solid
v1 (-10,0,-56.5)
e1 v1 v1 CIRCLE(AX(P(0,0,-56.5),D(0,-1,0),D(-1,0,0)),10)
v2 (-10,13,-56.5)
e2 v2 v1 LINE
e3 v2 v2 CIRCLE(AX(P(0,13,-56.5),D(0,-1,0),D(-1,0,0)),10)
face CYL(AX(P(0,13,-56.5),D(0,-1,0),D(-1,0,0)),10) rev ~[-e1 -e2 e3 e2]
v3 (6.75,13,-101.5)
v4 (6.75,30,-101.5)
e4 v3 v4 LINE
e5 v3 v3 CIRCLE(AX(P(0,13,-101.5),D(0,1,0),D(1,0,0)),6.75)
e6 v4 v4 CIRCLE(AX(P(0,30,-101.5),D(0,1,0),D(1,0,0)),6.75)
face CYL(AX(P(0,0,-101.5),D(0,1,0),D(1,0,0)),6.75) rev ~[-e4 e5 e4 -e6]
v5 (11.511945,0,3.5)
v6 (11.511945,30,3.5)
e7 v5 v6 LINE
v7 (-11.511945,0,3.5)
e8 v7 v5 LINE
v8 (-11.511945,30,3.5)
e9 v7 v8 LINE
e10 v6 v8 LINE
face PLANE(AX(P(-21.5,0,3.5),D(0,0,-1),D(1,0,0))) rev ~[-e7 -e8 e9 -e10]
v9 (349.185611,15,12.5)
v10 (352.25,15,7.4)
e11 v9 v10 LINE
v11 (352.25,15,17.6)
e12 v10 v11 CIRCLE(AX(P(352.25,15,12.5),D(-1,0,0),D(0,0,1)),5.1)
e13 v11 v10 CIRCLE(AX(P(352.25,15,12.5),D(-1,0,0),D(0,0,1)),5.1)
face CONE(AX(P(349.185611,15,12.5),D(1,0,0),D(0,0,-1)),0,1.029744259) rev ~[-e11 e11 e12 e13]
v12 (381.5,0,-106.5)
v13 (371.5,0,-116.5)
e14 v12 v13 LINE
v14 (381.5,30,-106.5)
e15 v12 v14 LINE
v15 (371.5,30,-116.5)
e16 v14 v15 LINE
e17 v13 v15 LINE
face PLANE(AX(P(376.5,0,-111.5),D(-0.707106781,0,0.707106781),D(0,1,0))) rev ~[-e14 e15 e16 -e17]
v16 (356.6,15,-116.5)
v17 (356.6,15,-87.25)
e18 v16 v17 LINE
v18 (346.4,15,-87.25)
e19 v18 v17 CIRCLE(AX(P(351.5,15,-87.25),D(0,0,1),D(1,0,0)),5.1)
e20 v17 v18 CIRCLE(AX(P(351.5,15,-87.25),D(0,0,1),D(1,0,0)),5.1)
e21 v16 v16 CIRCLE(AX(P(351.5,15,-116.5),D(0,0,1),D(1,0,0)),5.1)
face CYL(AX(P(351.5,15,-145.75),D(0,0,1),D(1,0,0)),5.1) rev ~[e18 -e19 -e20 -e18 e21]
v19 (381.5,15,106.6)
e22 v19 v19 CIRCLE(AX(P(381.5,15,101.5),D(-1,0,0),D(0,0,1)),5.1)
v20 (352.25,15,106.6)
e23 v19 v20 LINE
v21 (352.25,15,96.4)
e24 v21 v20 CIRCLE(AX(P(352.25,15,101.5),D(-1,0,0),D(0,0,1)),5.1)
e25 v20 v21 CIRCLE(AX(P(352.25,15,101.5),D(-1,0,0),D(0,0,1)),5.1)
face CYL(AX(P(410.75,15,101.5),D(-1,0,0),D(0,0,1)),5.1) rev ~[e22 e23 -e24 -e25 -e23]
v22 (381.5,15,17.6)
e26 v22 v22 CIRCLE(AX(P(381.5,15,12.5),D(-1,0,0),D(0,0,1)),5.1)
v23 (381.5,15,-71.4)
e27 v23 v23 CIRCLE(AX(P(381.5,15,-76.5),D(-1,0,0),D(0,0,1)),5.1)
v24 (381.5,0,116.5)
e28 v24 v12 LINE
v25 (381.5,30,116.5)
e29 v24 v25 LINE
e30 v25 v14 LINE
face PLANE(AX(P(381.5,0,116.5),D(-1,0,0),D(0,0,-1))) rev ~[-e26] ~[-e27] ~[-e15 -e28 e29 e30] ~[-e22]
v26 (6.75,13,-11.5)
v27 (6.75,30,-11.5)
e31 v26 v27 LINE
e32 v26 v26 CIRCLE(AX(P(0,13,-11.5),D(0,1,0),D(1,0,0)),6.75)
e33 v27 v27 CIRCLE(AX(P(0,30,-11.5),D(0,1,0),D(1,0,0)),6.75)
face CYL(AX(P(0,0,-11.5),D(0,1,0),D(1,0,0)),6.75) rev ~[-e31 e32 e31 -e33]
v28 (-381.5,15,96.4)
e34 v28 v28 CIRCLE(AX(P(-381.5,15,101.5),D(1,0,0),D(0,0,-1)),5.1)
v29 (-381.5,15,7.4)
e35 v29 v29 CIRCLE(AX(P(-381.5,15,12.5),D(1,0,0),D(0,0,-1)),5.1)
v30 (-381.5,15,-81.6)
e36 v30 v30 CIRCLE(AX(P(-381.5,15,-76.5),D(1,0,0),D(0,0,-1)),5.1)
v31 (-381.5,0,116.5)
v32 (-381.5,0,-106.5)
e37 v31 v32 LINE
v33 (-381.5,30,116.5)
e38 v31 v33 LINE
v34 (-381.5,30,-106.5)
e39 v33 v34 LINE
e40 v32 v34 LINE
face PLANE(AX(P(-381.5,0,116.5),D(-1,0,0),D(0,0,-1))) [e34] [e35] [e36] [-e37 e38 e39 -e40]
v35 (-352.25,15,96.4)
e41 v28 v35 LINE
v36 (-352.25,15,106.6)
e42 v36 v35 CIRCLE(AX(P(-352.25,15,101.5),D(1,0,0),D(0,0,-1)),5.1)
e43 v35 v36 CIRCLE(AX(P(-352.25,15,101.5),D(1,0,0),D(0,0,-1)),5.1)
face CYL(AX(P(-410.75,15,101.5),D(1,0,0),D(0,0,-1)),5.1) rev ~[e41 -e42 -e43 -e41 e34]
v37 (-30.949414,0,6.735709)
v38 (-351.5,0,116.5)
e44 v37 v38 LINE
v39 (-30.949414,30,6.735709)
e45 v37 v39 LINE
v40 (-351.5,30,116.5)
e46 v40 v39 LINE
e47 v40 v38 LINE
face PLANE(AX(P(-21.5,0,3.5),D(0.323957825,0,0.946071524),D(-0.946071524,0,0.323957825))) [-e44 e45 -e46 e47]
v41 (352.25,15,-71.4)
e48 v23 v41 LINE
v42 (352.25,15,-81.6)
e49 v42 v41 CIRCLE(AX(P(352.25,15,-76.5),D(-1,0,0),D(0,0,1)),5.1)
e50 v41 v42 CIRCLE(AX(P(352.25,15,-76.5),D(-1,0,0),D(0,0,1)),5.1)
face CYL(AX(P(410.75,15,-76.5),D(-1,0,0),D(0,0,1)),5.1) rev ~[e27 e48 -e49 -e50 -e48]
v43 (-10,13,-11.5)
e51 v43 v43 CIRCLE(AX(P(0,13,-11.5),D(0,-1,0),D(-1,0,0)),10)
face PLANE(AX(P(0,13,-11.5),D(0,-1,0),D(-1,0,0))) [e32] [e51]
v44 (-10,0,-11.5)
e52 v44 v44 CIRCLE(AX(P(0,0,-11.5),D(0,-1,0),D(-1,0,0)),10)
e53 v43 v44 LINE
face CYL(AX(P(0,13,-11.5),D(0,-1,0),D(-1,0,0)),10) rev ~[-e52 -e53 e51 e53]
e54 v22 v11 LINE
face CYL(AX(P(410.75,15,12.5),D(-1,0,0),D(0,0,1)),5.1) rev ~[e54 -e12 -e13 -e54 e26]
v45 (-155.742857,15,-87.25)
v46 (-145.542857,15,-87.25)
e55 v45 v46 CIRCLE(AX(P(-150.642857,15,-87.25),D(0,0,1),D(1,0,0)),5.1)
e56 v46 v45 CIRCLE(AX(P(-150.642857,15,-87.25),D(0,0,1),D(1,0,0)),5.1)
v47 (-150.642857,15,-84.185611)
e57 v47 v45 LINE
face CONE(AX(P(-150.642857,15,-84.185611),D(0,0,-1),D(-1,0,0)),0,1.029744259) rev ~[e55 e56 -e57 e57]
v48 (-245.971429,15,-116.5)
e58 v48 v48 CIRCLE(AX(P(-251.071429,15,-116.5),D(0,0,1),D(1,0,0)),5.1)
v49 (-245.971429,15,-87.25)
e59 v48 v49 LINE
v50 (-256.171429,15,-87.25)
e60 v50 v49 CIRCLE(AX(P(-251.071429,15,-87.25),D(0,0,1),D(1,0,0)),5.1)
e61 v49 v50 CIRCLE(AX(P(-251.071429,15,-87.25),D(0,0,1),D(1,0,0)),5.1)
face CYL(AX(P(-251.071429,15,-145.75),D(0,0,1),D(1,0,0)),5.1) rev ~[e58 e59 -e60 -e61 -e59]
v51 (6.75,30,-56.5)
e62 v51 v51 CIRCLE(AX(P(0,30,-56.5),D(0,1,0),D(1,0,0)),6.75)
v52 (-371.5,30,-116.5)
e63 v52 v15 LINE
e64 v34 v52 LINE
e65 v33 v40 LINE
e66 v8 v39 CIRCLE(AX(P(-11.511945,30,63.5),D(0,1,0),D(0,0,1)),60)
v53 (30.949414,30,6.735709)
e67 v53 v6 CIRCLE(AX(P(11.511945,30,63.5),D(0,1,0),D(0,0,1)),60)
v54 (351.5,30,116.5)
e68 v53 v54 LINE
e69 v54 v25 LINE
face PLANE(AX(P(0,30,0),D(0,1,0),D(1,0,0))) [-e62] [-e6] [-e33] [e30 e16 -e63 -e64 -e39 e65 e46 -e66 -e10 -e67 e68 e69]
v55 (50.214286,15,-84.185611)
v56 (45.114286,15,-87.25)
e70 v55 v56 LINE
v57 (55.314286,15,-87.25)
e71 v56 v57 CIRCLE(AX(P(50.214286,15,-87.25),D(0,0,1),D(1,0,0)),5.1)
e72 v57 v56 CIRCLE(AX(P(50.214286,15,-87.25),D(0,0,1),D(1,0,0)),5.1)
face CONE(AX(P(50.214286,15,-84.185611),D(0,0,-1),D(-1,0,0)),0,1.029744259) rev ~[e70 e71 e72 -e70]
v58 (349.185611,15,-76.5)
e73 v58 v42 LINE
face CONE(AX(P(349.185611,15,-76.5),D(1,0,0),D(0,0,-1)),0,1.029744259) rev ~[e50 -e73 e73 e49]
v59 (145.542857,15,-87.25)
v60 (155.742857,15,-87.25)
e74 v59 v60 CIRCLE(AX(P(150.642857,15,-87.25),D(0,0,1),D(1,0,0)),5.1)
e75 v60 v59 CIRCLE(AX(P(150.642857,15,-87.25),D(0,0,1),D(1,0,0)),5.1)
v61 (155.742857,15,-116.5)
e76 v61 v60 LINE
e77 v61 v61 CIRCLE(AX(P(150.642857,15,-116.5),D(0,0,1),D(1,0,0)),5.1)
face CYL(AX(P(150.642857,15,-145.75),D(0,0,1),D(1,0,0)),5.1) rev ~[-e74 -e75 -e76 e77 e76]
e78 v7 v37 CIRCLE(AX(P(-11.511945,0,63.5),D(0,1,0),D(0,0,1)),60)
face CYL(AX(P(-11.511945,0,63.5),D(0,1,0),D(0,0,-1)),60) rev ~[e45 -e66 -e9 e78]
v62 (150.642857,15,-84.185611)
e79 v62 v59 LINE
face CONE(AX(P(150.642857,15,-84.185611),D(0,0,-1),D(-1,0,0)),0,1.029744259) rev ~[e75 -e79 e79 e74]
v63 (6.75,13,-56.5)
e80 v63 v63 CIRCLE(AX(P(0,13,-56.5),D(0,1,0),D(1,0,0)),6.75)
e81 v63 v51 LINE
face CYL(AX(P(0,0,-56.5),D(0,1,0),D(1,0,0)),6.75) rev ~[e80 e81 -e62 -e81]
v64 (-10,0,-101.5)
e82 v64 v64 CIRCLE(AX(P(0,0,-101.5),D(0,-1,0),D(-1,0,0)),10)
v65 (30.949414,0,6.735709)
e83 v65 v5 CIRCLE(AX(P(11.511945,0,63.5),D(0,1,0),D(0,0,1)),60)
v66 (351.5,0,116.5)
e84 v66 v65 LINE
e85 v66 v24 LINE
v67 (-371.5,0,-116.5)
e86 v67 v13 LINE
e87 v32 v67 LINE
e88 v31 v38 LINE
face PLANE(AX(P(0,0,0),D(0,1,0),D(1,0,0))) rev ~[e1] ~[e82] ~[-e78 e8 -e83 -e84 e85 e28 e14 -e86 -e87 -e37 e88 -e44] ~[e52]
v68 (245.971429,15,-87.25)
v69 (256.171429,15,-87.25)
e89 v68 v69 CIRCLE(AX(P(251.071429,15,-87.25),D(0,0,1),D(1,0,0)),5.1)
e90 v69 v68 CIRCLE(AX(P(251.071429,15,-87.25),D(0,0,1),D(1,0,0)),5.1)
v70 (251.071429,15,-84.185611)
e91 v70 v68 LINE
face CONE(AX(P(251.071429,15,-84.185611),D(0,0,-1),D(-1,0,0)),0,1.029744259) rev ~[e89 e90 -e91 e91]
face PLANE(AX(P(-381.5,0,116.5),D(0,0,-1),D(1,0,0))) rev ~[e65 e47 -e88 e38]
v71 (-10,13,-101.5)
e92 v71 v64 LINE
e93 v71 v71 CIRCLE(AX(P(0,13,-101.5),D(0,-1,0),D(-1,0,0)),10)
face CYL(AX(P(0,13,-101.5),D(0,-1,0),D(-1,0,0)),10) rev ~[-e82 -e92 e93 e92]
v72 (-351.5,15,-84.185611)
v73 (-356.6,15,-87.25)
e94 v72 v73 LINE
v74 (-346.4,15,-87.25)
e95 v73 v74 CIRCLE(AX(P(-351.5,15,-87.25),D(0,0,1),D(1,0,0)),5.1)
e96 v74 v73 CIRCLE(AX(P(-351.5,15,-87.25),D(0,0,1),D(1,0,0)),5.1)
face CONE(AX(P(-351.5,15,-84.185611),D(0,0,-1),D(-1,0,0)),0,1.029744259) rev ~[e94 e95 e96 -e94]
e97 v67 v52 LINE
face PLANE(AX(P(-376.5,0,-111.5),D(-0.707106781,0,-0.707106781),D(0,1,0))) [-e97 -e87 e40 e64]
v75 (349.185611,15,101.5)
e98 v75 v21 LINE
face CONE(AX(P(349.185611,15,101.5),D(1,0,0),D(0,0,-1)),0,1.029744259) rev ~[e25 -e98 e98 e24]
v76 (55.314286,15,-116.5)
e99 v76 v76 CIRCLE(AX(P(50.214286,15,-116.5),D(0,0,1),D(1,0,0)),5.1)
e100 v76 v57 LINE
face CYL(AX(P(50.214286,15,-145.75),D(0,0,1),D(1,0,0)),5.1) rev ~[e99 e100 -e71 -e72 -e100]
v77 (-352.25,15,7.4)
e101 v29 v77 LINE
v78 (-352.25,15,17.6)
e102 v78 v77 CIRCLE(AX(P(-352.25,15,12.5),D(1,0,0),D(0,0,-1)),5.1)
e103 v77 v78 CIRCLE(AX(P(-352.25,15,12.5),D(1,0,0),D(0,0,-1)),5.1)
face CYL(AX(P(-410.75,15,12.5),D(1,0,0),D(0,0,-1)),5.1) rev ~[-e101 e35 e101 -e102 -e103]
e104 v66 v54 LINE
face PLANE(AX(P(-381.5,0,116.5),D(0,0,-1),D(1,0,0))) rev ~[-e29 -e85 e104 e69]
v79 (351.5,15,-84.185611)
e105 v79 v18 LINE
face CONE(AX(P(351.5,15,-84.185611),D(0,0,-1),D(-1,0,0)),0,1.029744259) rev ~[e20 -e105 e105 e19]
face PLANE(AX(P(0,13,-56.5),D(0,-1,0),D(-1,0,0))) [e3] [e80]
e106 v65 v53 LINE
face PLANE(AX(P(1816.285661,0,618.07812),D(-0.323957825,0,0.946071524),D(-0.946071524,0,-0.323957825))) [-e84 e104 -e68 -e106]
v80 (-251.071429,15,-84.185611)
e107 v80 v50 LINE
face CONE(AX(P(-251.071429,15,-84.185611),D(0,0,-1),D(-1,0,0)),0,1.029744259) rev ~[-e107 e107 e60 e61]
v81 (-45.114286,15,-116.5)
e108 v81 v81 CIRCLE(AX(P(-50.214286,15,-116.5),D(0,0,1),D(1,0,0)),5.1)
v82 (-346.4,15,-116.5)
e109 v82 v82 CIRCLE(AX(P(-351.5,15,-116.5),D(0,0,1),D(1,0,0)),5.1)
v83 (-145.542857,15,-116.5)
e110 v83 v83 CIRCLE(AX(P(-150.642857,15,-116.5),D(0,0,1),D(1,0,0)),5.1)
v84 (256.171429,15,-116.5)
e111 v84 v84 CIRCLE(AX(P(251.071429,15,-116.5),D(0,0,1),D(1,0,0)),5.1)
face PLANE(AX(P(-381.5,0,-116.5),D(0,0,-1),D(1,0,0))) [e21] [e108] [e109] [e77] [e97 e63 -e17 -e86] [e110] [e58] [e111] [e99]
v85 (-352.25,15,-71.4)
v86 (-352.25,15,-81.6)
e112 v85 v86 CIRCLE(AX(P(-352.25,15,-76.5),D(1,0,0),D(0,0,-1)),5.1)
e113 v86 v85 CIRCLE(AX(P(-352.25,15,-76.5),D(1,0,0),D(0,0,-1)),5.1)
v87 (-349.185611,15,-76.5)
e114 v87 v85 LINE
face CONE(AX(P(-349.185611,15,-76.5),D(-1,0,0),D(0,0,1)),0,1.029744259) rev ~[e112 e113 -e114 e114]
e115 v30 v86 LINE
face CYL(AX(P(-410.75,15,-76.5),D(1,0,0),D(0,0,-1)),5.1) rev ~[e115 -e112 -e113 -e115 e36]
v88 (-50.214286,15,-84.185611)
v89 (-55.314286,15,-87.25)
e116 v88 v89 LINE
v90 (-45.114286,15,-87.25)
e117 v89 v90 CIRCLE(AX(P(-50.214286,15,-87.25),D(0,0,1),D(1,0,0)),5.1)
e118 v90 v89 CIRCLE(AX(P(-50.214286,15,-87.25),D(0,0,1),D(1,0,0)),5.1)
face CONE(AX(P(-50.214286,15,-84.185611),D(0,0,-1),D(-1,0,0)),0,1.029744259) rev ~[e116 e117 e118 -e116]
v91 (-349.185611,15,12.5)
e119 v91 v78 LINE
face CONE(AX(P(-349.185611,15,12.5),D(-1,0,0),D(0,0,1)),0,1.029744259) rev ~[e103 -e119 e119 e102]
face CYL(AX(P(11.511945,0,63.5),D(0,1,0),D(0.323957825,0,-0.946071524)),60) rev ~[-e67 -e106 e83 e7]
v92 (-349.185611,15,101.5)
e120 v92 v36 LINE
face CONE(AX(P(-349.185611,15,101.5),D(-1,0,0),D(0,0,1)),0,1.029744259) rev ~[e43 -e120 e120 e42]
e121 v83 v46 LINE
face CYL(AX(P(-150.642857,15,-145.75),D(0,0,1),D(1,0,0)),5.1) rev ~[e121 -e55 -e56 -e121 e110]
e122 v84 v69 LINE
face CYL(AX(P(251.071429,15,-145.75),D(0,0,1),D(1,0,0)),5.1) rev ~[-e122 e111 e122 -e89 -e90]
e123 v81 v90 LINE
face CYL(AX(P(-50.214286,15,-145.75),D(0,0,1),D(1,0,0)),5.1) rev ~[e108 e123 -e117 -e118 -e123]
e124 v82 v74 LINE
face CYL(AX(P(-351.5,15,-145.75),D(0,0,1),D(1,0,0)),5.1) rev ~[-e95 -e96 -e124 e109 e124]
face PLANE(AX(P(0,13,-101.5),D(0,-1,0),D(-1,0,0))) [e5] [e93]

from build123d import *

# Parameters (mm, degrees)
SKETCH_1_W                = 763
SKETCH_1_H                = 233
EXTRUDE_1_DEPTH           = 30
CHAMFER_1_SIZE            = 10
CUT_EXTRUDE_1_DEPTH       = 401.018124589
CUT_EXTRUDE_1_DEPTH_BACK  = 30
FILLET_1_R                = 60
HOLE_WIZARD_1_D           = 13.5
HOLE_WIZARD_1_CBORE_D     = 20
HOLE_WIZARD_1_CBORE_DEPTH = 13
HOLE_WIZARD_M12_1_D       = 10.2
HOLE_WIZARD_M12_1_DEPTH   = 29.25
HOLE_WIZARD_M12_1_TIP     = 3.064389157
HOLE_WIZARD_M12_2_D       = 10.2
HOLE_WIZARD_M12_2_DEPTH   = 29.25
HOLE_WIZARD_M12_2_TIP     = 3.064389157
HOLE_WIZARD_M12_3_D       = 10.2
HOLE_WIZARD_M12_3_DEPTH   = 29.25
HOLE_WIZARD_M12_3_TIP     = 3.064389157


with BuildPart() as part:
    # 草图1 → 凸台-拉伸1 (new body)
    with BuildSketch(Plane(origin=(0, 0, 0), x_dir=(1, 0, 0), z_dir=(0, 1, 0))):
        Rectangle(SKETCH_1_W, SKETCH_1_H)
    extrude(amount=EXTRUDE_1_DEPTH)

    # 倒角1
    chamfer_1_edges = [part.edges().sort_by_distance(p)[0] for p in [
        (-381.5, 15, -116.5),
        (381.5, 15, -116.5),
    ]]
    chamfer(chamfer_1_edges, length=CHAMFER_1_SIZE)

    # 草图2 → 切除-拉伸1 (cut, two sides: drawn at the far end of the back side and taken through both)
    with BuildSketch(Plane(origin=(0, 30, 0), x_dir=(1, 0, 0), z_dir=(0, 1, 0)).offset(-CUT_EXTRUDE_1_DEPTH_BACK)):
        Polygon((-1816.285660926, -618.078120257), (-351.5, -116.5), (-21.5, -3.5), (21.5, -3.5), (351.5, -116.5), (1816.285660926, -618.078120257), (1816.285660926, -3714.642437803), (-1816.285660926, -3714.642437803), align=None)
    extrude(amount=CUT_EXTRUDE_1_DEPTH + CUT_EXTRUDE_1_DEPTH_BACK, mode=Mode.SUBTRACT)

    # 圆角1
    fillet_1_edges = [part.edges().sort_by_distance(p)[0] for p in [
        (21.5, 15, 3.5),
        (-21.5, 15, 3.5),
    ]]
    fillet(fillet_1_edges, radius=FILLET_1_R)

    # 打孔尺寸(%根据)内六角圆柱头螺钉的类型1 (through all)
    with Locations(Plane(origin=(0, 0, 0), x_dir=(-1, 0, 0), z_dir=(0, -1, 0))):
        with Locations((0, 11.5), (0, 56.5), (0, 101.5)):
            CounterBoreHole(HOLE_WIZARD_1_D / 2, HOLE_WIZARD_1_CBORE_D / 2, HOLE_WIZARD_1_CBORE_DEPTH)

    # M12 螺纹孔1
    with Locations(Plane(origin=(0, 0, -116.5), x_dir=(-1, 0, 0), z_dir=(0, 0, -1))):
        with Locations((351.5, 15), (251.071428571, 15), (150.642857143, 15), (50.214285714, 15), (-50.214285714, 15), (-150.642857143, 15), (-251.071428571, 15), (-351.5, 15)):
            Hole(HOLE_WIZARD_M12_1_D / 2, depth=HOLE_WIZARD_M12_1_DEPTH)
            with Locations((0, 0, -(HOLE_WIZARD_M12_1_DEPTH + HOLE_WIZARD_M12_1_TIP / 2))):  # 118° drill point
                Cone(0, HOLE_WIZARD_M12_1_D / 2, HOLE_WIZARD_M12_1_TIP, mode=Mode.SUBTRACT)

    # M12 螺纹孔2
    with Locations(Plane.ZY.offset(381.5)):
        with Locations((-76.5, 15), (12.5, 15), (101.5, 15)):
            Hole(HOLE_WIZARD_M12_2_D / 2, depth=HOLE_WIZARD_M12_2_DEPTH)
            with Locations((0, 0, -(HOLE_WIZARD_M12_2_DEPTH + HOLE_WIZARD_M12_2_TIP / 2))):  # 118° drill point
                Cone(0, HOLE_WIZARD_M12_2_D / 2, HOLE_WIZARD_M12_2_TIP, mode=Mode.SUBTRACT)

    # M12 螺纹孔3
    with Locations(Plane(origin=(381.5, 0, 0), x_dir=(0, 0, -1), z_dir=(1, 0, 0))):
        with Locations((76.5, 15), (-12.5, 15), (-101.5, 15)):
            Hole(HOLE_WIZARD_M12_3_D / 2, depth=HOLE_WIZARD_M12_3_DEPTH)
            with Locations((0, 0, -(HOLE_WIZARD_M12_3_DEPTH + HOLE_WIZARD_M12_3_TIP / 2))):  # 118° drill point
                Cone(0, HOLE_WIZARD_M12_3_D / 2, HOLE_WIZARD_M12_3_TIP, mode=Mode.SUBTRACT)


solid = part.part
